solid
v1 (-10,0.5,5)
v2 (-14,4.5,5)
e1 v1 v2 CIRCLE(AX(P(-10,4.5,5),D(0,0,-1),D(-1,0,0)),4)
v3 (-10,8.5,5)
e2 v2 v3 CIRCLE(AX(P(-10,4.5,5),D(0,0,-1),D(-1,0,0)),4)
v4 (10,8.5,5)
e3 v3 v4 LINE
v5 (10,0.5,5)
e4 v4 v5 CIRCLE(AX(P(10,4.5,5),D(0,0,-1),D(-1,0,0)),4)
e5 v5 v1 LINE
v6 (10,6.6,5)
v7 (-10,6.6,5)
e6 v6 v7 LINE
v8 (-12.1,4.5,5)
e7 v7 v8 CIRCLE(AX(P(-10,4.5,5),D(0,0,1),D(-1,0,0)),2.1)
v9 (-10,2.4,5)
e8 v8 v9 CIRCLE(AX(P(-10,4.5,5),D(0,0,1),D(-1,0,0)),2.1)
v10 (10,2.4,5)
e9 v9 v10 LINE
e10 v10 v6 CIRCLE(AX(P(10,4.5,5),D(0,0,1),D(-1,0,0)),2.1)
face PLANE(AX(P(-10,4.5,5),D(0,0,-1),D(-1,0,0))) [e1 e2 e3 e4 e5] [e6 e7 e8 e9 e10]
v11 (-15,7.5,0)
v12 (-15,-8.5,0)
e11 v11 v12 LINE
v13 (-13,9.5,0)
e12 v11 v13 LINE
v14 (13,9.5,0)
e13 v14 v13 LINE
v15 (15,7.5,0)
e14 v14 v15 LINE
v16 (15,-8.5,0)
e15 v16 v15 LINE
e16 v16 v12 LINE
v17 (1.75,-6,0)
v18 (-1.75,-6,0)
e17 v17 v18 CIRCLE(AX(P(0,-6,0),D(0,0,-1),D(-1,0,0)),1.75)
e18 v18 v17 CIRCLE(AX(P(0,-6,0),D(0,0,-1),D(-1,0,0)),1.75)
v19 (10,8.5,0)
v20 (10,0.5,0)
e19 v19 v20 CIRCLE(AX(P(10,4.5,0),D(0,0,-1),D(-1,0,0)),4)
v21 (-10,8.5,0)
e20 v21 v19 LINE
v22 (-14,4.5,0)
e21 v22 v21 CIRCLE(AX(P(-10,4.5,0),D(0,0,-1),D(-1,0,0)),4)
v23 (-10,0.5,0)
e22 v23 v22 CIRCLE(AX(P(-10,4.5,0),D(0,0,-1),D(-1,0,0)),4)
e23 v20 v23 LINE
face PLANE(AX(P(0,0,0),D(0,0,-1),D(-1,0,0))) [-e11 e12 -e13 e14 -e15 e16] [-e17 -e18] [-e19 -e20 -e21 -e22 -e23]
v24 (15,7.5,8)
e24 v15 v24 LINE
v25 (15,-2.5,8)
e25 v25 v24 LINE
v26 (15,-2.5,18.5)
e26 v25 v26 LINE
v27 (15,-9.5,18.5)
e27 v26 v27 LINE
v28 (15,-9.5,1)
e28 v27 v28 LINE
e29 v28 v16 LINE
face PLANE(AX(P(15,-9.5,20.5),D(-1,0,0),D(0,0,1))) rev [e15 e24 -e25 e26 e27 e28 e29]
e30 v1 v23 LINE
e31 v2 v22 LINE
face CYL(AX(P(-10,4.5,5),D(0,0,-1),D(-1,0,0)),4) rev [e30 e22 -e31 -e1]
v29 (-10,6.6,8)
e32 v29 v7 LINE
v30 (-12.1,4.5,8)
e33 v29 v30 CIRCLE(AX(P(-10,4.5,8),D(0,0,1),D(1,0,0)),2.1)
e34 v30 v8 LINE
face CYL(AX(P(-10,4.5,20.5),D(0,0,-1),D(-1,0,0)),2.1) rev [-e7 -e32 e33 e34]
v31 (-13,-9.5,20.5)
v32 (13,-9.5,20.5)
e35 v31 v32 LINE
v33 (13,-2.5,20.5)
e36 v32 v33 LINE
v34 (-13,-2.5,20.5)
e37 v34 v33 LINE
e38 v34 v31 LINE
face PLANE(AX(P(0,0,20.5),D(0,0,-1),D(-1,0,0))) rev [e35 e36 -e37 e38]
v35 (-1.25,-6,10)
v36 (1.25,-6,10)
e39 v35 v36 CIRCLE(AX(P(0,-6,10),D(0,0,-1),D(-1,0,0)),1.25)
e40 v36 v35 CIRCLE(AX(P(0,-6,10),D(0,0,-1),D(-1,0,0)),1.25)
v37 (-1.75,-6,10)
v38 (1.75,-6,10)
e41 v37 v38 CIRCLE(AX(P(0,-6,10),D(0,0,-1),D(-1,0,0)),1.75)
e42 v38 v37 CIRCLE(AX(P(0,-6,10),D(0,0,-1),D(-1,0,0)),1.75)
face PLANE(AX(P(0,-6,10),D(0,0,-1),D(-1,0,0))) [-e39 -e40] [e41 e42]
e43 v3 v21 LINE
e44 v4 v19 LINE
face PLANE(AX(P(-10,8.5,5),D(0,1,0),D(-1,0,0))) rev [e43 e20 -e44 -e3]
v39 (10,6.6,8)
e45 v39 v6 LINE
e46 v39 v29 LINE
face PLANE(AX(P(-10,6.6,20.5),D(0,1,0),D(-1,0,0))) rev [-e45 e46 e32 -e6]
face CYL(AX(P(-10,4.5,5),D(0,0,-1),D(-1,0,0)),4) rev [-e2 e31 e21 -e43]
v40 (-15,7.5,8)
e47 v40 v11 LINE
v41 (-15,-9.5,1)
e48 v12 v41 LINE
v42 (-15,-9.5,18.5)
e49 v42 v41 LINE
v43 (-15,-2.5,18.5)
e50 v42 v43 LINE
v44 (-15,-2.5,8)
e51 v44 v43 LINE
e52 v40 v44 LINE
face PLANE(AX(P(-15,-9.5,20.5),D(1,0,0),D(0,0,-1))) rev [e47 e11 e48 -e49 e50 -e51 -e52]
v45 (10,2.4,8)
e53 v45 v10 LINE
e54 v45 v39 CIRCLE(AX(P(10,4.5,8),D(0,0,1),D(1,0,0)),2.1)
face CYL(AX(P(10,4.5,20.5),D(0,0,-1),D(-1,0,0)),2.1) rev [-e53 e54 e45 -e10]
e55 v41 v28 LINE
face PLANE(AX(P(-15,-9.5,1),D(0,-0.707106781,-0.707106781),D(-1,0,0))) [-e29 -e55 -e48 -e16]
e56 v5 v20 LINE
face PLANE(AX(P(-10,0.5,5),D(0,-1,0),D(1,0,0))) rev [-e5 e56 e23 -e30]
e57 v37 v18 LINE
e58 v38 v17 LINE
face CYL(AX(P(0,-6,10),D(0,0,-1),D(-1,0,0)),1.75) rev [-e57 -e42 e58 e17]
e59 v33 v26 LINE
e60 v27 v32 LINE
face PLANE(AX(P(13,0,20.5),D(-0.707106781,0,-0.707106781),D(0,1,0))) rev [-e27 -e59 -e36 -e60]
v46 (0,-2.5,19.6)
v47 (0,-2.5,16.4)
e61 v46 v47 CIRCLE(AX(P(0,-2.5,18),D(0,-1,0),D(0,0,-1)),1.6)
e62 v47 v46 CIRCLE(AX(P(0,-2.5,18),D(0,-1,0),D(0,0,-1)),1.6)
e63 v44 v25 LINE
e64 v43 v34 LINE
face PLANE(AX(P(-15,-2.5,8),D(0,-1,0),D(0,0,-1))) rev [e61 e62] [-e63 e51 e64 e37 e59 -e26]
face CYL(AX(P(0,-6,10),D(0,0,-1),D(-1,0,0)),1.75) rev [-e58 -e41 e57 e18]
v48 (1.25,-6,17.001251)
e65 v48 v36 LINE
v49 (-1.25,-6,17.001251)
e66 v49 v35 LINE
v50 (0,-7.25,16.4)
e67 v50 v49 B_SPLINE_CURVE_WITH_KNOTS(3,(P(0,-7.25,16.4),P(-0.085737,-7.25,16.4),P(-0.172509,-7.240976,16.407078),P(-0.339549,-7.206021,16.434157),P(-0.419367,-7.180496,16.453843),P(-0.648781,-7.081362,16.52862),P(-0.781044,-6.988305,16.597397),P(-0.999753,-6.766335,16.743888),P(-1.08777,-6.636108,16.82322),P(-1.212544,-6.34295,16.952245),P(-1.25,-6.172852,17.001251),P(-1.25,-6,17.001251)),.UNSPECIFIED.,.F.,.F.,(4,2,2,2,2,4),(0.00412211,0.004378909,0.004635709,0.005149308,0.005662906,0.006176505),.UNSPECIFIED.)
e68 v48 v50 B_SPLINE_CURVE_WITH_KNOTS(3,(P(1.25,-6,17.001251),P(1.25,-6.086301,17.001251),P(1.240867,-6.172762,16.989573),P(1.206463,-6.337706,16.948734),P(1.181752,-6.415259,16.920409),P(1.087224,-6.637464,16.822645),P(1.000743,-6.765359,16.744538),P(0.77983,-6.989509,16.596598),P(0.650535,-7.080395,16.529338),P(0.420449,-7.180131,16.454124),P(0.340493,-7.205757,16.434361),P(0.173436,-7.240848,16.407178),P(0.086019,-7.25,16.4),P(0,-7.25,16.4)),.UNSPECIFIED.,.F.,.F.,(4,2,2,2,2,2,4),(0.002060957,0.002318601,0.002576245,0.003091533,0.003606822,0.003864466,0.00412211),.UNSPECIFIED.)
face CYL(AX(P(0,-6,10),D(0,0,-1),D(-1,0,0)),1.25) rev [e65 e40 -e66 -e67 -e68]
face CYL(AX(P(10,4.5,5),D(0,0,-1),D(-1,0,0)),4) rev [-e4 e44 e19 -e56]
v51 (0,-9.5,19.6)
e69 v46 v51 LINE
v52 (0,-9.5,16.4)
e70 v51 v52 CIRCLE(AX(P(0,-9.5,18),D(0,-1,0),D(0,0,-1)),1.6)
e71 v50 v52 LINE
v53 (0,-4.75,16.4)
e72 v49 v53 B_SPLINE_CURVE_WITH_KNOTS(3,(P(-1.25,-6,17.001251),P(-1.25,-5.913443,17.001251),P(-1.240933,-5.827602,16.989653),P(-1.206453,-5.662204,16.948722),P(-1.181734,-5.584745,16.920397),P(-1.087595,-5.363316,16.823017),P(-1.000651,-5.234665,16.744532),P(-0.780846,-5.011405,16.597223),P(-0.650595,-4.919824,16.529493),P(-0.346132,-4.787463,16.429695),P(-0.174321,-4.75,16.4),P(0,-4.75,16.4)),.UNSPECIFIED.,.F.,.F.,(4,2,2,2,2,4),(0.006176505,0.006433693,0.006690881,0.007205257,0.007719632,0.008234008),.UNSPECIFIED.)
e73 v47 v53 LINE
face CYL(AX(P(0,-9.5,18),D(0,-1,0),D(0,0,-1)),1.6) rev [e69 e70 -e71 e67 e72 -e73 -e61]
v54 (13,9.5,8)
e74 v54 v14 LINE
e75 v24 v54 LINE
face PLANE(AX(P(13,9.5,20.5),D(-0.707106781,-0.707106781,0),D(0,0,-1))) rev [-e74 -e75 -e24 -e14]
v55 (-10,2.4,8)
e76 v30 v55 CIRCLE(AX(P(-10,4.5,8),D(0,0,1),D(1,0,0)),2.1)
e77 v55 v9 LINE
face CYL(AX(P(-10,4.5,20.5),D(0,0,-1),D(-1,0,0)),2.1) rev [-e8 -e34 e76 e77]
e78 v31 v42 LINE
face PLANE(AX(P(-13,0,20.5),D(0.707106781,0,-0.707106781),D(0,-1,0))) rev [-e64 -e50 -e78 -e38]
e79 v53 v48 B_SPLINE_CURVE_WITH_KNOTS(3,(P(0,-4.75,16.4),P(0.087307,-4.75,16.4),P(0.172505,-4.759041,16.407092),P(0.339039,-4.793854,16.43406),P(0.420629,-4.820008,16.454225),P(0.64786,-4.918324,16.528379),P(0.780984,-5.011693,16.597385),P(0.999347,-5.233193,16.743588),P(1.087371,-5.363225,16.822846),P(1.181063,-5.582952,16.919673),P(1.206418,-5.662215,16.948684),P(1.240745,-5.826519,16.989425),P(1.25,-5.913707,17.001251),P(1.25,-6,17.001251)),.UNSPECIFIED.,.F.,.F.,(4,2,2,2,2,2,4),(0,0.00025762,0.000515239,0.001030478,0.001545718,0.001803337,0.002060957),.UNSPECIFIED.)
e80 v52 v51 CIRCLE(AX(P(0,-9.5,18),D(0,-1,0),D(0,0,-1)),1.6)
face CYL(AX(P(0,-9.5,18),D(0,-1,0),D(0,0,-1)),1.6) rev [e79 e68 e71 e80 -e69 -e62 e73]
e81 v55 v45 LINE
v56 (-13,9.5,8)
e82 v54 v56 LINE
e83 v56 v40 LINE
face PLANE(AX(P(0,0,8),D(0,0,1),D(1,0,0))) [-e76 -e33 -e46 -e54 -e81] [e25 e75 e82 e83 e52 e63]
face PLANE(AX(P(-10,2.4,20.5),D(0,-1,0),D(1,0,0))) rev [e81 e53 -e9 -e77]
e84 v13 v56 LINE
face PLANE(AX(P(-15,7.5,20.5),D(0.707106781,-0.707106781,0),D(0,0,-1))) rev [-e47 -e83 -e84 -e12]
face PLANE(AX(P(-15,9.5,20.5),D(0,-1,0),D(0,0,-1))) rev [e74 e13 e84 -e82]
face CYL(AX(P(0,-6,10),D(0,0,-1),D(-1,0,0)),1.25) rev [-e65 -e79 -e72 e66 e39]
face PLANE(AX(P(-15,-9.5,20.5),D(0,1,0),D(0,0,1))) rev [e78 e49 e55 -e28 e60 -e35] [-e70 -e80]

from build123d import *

# Parameters (mm, degrees)
SKETCH_1_W                = 30
SKETCH_1_H                = 19
EXTRUDE_1_DEPTH           = 20.5
SKETCH_2_W                = 30
SKETCH_2_H                = 12
CUT_EXTRUDE_1_DEPTH       = 12.5
CUT_EXTRUDE_2_DEPTH       = 28.120103245
CUT_EXTRUDE_3_DEPTH       = 5
SKETCH_5_R                = 1.75
CUT_EXTRUDE_4_DEPTH       = 10
HOLE_WIZARD_M3_1_D        = 3.2
HOLE_WIZARD_M3_1_2_REACH  = 22.628
HOLE_WIZARD_M3_1_2_BORE_R = 1.25
CHAMFER_1_SIZE            = 2
CHAMFER_2_SIZE            = 1


with BuildPart() as part:
    # 草图1 → 凸台-拉伸1 (new body)
    with BuildSketch(Plane.XY):
        Rectangle(SKETCH_1_W, SKETCH_1_H)
    extrude(amount=EXTRUDE_1_DEPTH)

    # 草图2 → 切除-拉伸1 (cut)
    with BuildSketch(Plane.XY.offset(20.5)):
        with Locations((0, 3.5)):
            Rectangle(SKETCH_2_W, SKETCH_2_H)
    extrude(amount=-CUT_EXTRUDE_1_DEPTH, mode=Mode.SUBTRACT)

    # 草图3 → 切除-拉伸2 (cut, through all)
    with BuildSketch(Plane(origin=(0, 0, 0), x_dir=(-1, 0, 0), z_dir=(0, 0, -1))):
        with BuildLine():
            Line((10, 2.4), (-10, 2.4))
            ThreePointArc((-10, 2.4), (-12.1, 4.5), (-10, 6.6))
            Line((-10, 6.6), (10, 6.6))
            ThreePointArc((10, 6.6), (12.1, 4.5), (10, 2.4))
        make_face()
    extrude(amount=-CUT_EXTRUDE_2_DEPTH, mode=Mode.SUBTRACT)

    # 草图4 → 切除-拉伸3 (cut)
    with BuildSketch(Plane(origin=(0, 0, 0), x_dir=(-1, 0, 0), z_dir=(0, 0, -1))):
        with BuildLine():
            Line((10, 0.5), (-10, 0.5))
            ThreePointArc((-10, 0.5), (-14, 4.5), (-10, 8.5))
            Line((-10, 8.5), (10, 8.5))
            ThreePointArc((10, 8.5), (14, 4.5), (10, 0.5))
        make_face()
    extrude(amount=-CUT_EXTRUDE_3_DEPTH, mode=Mode.SUBTRACT)

    # 草图5 → 切除-拉伸4 (cut)
    with BuildSketch(Plane(origin=(0, 0, 0), x_dir=(-1, 0, 0), z_dir=(0, 0, -1))):
        with Locations((0, -6)):
            Circle(SKETCH_5_R)
    extrude(amount=-CUT_EXTRUDE_4_DEPTH, mode=Mode.SUBTRACT)

    # Hole Wizard M3 _1 (through all)
    with Locations(Plane(origin=(0, -9.5, 0), x_dir=(-1, 0, 0), z_dir=(0, -1, 0))):
        with Locations((0, -18)):
            Hole(HOLE_WIZARD_M3_1_D / 2)

    # Hole Wizard M3 _1 2 bore → Hole Wizard M3 _1 2 (cut, up to next)
    with BuildSketch(Plane(origin=(0, 0, 10), x_dir=(-1, 0, 0), z_dir=(0, 0, -1)), mode=Mode.PRIVATE) as hole_wizard_m3_1_2_sk1:
        with Locations((0, -6)):
            Circle(HOLE_WIZARD_M3_1_2_BORE_R)
    hole_wizard_m3_1_2_tool1 = extrude(hole_wizard_m3_1_2_sk1.sketch, amount=-HOLE_WIZARD_M3_1_2_REACH, mode=Mode.PRIVATE) & part.part
    add(hole_wizard_m3_1_2_tool1.solids().sort_by_distance((0, -6, 10))[0], mode=Mode.SUBTRACT)

    # 倒角1
    chamfer_1_edges = [part.edges().sort_by_distance(p)[0] for p in [
        (-15, -6, 20.5),
        (-15, 9.5, 4),
        (15, 9.5, 4),
        (15, -6, 20.5),
    ]]
    chamfer(chamfer_1_edges, length=CHAMFER_1_SIZE)

    # 倒角2
    chamfer_2_edges = [part.edges().sort_by_distance(p)[0] for p in [
        (0, -9.5, 0),
    ]]
    chamfer(chamfer_2_edges, length=CHAMFER_2_SIZE)


solid = part.part
